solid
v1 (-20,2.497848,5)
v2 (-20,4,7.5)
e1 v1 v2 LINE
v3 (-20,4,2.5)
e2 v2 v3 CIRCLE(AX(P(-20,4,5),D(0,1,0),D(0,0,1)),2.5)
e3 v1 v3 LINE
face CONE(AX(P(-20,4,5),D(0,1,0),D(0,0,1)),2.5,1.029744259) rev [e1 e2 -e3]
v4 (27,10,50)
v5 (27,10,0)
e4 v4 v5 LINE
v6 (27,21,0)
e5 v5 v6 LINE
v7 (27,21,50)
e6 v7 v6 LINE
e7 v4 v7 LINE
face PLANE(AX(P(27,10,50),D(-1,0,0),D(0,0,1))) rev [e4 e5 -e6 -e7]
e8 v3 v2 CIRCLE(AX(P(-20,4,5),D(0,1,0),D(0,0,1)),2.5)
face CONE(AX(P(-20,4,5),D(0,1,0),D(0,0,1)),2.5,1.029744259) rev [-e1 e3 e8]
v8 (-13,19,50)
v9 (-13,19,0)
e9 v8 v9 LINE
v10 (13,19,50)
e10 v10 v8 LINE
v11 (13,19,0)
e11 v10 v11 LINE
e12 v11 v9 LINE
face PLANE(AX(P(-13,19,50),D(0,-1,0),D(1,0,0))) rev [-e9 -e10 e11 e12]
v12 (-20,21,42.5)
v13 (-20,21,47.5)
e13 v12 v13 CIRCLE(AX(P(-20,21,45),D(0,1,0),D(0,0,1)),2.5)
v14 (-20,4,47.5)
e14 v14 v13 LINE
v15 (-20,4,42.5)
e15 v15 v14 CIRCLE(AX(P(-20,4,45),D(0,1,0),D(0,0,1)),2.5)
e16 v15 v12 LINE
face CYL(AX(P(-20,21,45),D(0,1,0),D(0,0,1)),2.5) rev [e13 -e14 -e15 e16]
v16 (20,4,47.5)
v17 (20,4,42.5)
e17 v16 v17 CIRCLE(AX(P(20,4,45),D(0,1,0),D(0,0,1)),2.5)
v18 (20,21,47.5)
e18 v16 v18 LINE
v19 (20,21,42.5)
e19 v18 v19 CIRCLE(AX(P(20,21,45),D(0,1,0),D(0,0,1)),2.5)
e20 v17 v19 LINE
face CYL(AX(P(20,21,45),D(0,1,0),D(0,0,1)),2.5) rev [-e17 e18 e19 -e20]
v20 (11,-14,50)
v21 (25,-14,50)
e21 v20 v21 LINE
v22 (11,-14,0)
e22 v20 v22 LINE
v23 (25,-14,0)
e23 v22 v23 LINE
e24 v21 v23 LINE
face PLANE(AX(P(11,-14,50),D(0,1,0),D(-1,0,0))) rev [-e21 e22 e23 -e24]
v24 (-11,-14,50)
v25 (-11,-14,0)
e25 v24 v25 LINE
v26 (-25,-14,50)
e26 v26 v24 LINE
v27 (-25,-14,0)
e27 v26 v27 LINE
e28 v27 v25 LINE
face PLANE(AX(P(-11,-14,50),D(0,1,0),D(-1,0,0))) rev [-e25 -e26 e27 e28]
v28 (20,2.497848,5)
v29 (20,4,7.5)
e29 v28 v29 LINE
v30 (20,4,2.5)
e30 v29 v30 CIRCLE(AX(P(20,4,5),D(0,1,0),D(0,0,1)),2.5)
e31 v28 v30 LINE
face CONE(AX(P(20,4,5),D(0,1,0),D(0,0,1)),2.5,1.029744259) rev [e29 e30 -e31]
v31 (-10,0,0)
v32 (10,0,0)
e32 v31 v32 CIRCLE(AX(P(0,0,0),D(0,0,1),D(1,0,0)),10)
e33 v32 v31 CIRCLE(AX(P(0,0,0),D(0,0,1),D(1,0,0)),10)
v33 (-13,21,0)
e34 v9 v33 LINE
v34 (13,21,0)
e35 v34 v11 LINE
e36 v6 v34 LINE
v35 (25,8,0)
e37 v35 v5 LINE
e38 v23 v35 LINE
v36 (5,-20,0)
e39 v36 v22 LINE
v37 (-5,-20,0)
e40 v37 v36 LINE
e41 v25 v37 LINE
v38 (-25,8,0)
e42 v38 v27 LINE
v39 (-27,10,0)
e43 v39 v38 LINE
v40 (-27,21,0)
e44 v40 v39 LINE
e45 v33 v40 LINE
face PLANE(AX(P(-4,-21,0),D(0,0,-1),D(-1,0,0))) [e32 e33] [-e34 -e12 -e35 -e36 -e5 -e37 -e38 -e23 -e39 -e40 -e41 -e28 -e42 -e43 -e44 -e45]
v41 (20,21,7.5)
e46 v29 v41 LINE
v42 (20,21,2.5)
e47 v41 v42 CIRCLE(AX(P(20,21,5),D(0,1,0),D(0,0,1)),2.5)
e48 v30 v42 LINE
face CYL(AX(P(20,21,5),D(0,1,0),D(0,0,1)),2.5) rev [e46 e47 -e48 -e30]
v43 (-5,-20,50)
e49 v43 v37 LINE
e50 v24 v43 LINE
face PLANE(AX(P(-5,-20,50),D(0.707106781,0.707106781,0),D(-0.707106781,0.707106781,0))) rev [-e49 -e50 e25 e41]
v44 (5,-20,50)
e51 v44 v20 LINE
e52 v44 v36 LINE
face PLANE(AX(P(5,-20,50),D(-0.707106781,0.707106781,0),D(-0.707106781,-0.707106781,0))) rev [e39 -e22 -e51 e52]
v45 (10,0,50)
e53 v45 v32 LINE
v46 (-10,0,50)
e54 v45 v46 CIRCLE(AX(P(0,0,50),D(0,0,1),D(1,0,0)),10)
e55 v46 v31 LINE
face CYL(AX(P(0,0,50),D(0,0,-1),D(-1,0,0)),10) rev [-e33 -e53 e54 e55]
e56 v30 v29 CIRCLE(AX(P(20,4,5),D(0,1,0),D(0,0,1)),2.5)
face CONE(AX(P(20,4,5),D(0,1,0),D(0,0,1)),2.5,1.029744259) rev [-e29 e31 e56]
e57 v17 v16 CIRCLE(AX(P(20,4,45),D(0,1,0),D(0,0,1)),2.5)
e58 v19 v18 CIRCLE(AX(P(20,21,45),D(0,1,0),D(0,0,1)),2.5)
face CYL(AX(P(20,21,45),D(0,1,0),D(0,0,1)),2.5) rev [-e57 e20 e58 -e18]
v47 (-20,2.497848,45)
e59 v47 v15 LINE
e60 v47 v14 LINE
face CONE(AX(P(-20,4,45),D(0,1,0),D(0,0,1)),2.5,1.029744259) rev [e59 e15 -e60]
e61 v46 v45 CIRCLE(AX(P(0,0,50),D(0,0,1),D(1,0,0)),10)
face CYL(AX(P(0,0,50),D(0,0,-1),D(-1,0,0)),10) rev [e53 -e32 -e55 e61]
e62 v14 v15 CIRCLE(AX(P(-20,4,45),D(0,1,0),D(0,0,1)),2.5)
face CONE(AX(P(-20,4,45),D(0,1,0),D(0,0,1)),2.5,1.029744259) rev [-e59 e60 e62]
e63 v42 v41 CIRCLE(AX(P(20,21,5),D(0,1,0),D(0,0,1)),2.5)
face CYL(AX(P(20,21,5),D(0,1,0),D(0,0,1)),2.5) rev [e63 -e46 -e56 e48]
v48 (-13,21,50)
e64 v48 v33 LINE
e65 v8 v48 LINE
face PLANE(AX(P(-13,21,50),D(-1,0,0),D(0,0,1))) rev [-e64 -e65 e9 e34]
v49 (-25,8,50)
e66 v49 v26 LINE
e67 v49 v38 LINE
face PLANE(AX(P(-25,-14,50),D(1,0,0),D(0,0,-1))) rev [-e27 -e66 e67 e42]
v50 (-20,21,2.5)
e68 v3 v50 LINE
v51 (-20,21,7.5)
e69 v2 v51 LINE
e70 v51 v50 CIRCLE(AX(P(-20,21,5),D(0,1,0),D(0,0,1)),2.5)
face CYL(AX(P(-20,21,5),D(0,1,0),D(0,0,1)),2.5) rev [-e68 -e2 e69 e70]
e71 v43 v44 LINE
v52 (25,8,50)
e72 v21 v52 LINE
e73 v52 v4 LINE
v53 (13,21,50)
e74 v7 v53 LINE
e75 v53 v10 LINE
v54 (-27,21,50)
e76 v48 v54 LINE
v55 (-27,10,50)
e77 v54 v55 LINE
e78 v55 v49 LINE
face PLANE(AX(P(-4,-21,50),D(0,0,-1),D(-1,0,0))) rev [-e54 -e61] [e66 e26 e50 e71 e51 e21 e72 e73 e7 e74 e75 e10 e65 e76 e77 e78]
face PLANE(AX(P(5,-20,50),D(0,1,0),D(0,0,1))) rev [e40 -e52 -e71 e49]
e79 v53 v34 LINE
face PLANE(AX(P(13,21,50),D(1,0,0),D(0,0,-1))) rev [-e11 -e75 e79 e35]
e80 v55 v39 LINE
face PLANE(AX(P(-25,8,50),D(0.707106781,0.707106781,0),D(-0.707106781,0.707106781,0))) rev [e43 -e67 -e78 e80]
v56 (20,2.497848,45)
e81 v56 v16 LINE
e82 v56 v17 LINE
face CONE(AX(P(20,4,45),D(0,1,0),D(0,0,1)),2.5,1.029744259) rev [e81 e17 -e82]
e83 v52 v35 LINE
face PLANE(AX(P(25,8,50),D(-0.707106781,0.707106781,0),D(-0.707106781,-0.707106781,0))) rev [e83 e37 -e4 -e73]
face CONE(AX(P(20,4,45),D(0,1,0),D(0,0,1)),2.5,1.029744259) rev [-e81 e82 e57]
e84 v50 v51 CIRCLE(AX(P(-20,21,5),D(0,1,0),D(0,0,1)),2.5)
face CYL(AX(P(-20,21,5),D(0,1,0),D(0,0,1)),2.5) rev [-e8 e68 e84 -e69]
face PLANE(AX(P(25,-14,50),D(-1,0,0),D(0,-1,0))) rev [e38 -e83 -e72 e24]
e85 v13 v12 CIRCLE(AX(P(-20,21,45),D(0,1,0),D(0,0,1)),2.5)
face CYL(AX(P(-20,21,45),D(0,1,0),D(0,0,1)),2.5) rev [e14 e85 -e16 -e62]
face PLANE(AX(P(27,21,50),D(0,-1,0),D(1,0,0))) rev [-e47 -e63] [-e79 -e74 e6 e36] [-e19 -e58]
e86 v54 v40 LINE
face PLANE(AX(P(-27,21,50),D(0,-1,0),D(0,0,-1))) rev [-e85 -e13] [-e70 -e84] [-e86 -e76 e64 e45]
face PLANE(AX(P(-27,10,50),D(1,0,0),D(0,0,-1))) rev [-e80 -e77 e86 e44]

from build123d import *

# Parameters (mm, degrees)
SKETCH_1_R                  = 10
EXTRUDE_1_DEPTH             = 50
PATTERN_LINEAR_1_COUNT      = 2
PATTERN_LINEAR_1_PITCH      = 40
PATTERN_LINEAR_1_COUNT_DIR2 = 2
PATTERN_LINEAR_1_PITCH_DIR2 = 40


with BuildPart() as part:
    # 草图1 → 拉伸1 (new body)
    with BuildSketch(Plane.XY):
        Polygon((5, -20), (-5, -20), (-11, -14), (-25, -14), (-25, 8), (-27, 10), (-27, 21), (-13, 21), (-13, 19), (13, 19), (13, 21), (27, 21), (27, 10), (25, 8), (25, -14), (11, -14), align=None)
        Circle(SKETCH_1_R, mode=Mode.SUBTRACT)
    extrude(amount=EXTRUDE_1_DEPTH)

    # 草图2 → M6x1.0 螺纹孔1 (revolve, cut)
    with BuildSketch(Plane(origin=(20, 21, 5), x_dir=(0, 0, 1), z_dir=(1, 0, 0))):
        Polygon((0, 0), (0, 18.502151548), (2.5, 17), (2.5, 0), align=None)
    m6x1_0_1 = revolve(axis=Axis((20, 27.35, 5), (0, -1, 0)), mode=Mode.SUBTRACT)

    # 阵列(线性)1: M6x1.0 _1 2 × 2
    with Locations(*[(-j * PATTERN_LINEAR_1_PITCH_DIR2, 0, i * PATTERN_LINEAR_1_PITCH) for i in range(PATTERN_LINEAR_1_COUNT) for j in range(PATTERN_LINEAR_1_COUNT_DIR2) if (i, j) != (0, 0)]):
        add(m6x1_0_1, mode=Mode.SUBTRACT)


solid = part.part
